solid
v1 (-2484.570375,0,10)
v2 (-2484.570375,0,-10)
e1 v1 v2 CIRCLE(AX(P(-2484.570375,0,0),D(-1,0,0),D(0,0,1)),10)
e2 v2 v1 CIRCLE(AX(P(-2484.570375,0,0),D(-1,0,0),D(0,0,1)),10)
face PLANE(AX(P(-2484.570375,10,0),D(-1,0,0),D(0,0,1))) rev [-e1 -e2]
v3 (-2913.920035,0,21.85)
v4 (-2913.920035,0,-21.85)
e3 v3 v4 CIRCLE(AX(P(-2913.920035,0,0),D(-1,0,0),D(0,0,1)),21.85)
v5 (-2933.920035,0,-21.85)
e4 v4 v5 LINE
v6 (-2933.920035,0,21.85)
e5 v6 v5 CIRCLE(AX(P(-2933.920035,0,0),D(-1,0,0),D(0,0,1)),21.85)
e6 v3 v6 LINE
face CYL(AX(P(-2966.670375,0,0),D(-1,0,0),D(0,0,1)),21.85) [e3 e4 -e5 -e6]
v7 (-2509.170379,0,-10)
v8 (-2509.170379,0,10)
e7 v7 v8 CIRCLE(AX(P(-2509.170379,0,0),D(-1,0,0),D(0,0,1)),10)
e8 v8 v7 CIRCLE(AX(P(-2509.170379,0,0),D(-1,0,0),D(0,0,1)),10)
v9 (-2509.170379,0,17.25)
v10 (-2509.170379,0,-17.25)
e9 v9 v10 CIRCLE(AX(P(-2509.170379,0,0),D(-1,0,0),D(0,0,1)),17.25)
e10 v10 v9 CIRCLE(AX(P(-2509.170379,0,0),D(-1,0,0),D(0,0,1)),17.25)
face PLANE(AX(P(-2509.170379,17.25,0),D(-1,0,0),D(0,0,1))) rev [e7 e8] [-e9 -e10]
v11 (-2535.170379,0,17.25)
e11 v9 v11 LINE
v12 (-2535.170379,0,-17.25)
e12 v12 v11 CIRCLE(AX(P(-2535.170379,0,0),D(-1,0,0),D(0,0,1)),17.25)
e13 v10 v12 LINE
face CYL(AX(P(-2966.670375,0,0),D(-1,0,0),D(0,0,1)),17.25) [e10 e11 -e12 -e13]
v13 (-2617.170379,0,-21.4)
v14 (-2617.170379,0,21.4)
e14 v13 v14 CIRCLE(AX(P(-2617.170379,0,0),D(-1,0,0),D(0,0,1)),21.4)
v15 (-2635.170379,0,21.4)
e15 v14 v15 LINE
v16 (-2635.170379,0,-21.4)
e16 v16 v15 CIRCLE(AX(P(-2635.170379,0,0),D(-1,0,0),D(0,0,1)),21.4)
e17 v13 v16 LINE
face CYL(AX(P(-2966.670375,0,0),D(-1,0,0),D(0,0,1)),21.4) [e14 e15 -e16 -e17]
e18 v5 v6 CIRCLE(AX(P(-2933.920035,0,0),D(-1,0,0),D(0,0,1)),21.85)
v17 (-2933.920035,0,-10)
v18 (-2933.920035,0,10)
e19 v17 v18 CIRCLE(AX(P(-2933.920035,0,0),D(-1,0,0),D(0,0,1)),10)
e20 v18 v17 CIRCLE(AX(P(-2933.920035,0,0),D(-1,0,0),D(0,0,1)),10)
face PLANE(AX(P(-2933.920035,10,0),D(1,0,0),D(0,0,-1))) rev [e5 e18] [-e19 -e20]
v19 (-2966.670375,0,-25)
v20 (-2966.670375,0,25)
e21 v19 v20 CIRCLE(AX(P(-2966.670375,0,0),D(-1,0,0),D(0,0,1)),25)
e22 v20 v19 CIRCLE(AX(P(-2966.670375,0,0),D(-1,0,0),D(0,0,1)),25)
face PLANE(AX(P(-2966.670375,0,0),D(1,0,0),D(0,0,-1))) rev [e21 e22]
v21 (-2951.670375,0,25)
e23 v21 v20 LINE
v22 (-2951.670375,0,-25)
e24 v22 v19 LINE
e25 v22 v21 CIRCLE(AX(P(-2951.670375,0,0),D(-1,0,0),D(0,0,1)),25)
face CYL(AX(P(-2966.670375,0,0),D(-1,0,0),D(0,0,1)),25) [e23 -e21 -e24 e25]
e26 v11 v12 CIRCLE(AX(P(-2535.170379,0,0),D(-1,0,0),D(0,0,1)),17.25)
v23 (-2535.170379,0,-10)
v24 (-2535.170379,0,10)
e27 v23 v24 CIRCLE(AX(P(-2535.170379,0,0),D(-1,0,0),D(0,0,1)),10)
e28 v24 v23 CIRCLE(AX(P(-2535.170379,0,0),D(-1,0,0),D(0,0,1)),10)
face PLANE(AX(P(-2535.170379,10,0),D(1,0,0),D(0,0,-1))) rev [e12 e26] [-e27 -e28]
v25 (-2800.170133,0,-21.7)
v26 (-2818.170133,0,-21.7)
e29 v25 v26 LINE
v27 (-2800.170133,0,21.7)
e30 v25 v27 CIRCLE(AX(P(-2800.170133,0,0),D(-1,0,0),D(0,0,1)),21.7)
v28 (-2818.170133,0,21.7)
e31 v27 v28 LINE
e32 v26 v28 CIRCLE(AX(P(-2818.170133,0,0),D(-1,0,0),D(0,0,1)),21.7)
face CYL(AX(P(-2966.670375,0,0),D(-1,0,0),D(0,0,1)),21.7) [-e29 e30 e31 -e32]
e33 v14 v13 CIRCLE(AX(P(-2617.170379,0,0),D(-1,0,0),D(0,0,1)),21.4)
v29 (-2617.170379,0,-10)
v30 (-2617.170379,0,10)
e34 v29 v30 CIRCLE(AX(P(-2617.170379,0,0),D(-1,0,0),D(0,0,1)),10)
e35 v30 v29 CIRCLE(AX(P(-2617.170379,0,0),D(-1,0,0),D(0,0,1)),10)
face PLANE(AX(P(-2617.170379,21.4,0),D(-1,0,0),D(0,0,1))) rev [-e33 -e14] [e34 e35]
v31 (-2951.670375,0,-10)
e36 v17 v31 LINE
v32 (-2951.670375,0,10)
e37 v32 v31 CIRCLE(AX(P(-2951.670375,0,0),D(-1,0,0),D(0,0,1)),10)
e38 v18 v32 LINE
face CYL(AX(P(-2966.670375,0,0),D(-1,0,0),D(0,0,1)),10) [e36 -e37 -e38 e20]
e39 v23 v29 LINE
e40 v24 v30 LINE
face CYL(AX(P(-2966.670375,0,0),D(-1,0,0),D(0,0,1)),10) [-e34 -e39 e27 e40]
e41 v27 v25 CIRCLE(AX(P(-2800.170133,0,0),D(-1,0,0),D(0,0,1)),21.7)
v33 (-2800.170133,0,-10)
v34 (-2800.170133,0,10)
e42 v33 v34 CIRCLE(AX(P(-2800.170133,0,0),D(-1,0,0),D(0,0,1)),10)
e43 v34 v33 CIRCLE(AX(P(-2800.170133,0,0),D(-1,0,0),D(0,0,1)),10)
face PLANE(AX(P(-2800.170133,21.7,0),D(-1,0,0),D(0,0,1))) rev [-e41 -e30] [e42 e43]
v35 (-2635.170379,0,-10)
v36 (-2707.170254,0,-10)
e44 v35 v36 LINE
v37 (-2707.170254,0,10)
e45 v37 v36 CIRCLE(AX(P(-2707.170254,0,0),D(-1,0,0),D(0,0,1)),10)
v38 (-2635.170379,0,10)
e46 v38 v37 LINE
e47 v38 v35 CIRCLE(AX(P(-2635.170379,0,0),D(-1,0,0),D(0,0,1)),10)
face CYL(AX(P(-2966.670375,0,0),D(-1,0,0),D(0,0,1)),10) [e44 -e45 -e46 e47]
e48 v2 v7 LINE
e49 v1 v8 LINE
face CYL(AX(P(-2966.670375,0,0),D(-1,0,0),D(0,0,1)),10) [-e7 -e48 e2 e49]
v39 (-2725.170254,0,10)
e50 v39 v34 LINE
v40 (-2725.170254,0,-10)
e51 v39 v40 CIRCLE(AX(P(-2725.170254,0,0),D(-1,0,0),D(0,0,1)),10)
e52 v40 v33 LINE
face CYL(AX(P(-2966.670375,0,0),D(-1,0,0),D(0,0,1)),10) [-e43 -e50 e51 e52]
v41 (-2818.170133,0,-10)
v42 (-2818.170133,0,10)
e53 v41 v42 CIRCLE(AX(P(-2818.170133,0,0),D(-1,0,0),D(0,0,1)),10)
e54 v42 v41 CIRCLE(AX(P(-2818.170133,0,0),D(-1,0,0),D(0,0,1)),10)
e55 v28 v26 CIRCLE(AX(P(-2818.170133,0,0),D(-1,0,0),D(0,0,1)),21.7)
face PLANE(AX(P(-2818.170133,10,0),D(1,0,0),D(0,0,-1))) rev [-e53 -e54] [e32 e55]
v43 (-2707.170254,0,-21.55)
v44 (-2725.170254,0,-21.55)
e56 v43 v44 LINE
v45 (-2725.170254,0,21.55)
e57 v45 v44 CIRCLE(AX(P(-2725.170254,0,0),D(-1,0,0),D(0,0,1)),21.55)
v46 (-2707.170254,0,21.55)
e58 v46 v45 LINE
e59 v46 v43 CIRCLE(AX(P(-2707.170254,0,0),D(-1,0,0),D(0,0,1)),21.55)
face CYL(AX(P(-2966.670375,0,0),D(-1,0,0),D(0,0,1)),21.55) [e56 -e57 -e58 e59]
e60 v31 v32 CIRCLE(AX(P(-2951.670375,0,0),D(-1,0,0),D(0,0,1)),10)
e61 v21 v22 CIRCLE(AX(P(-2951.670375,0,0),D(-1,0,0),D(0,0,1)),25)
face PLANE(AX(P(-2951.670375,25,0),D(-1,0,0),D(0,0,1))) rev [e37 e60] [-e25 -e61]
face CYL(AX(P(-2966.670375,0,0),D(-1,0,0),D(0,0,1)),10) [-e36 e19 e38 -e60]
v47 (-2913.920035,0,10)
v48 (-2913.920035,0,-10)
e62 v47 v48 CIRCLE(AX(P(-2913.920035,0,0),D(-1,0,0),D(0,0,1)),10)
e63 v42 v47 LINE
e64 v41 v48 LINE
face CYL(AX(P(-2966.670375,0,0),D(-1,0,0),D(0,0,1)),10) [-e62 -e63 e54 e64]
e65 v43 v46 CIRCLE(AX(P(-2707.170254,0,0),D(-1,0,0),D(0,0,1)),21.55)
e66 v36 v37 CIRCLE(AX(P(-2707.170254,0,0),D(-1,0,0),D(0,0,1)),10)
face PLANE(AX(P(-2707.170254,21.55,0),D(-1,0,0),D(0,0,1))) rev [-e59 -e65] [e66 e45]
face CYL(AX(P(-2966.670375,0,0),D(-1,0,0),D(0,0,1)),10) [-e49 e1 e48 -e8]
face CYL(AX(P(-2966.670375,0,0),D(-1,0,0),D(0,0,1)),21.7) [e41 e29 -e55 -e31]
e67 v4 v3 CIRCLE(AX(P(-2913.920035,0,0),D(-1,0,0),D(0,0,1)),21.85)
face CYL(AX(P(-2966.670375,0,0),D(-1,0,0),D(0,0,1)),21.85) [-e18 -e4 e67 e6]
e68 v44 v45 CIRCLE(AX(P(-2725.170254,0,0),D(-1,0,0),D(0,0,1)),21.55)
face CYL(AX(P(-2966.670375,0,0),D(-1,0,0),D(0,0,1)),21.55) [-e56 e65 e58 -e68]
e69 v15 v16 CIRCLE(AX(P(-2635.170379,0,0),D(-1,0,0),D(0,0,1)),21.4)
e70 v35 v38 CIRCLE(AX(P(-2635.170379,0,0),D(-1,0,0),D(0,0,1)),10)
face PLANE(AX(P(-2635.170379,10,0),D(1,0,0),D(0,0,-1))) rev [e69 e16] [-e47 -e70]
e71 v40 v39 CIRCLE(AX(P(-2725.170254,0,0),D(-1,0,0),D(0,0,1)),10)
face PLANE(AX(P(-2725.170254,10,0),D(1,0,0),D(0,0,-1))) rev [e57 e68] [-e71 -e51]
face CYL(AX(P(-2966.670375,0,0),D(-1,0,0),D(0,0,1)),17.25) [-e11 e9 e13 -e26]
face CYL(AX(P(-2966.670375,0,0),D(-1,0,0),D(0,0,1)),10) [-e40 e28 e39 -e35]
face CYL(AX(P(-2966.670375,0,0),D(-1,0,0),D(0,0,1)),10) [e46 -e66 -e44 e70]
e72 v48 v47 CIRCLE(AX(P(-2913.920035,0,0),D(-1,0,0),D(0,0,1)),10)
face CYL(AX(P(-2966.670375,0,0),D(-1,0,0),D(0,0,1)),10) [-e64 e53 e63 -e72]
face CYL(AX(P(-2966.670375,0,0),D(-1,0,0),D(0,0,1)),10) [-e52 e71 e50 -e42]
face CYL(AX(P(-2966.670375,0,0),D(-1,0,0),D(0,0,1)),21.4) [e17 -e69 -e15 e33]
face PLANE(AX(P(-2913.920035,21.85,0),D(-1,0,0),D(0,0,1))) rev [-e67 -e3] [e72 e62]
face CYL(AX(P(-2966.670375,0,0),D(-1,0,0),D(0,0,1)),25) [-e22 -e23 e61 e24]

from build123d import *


with BuildPart() as part:
    # Sketch1 → Revolve1 (revolve)
    with BuildSketch(Plane.XY, mode=Mode.PRIVATE) as revolve1_sk:
        Polygon((-2966.670374904, 0), (-2484.570374904, 0), (-2484.570374904, 10), (-2509.170378936, 10), (-2509.170378936, 17.25), (-2535.170378936, 17.25), (-2535.170378936, 10), (-2617.170378936, 10), (-2617.170378936, 21.4), (-2635.170378936, 21.4), (-2635.170378936, 10), (-2707.170253936, 10), (-2707.170253936, 21.55), (-2725.170253936, 21.55), (-2725.170253936, 10), (-2800.170132968, 10), (-2800.170132968, 21.7), (-2818.170132968, 21.7), (-2818.170132968, 10), (-2913.920034929, 10), (-2913.920034929, 21.85), (-2933.920034929, 21.85), (-2933.920034929, 10), (-2951.670374904, 10), (-2951.670374904, 25), (-2966.670374904, 25), align=None)
    revolve(revolve1_sk.sketch.rotate(Axis((-2966.670374904, 0, 0), (1, 0, 0)), 90), axis=Axis((-2966.670374904, 0, 0), (1, 0, 0)))


solid = part.part
